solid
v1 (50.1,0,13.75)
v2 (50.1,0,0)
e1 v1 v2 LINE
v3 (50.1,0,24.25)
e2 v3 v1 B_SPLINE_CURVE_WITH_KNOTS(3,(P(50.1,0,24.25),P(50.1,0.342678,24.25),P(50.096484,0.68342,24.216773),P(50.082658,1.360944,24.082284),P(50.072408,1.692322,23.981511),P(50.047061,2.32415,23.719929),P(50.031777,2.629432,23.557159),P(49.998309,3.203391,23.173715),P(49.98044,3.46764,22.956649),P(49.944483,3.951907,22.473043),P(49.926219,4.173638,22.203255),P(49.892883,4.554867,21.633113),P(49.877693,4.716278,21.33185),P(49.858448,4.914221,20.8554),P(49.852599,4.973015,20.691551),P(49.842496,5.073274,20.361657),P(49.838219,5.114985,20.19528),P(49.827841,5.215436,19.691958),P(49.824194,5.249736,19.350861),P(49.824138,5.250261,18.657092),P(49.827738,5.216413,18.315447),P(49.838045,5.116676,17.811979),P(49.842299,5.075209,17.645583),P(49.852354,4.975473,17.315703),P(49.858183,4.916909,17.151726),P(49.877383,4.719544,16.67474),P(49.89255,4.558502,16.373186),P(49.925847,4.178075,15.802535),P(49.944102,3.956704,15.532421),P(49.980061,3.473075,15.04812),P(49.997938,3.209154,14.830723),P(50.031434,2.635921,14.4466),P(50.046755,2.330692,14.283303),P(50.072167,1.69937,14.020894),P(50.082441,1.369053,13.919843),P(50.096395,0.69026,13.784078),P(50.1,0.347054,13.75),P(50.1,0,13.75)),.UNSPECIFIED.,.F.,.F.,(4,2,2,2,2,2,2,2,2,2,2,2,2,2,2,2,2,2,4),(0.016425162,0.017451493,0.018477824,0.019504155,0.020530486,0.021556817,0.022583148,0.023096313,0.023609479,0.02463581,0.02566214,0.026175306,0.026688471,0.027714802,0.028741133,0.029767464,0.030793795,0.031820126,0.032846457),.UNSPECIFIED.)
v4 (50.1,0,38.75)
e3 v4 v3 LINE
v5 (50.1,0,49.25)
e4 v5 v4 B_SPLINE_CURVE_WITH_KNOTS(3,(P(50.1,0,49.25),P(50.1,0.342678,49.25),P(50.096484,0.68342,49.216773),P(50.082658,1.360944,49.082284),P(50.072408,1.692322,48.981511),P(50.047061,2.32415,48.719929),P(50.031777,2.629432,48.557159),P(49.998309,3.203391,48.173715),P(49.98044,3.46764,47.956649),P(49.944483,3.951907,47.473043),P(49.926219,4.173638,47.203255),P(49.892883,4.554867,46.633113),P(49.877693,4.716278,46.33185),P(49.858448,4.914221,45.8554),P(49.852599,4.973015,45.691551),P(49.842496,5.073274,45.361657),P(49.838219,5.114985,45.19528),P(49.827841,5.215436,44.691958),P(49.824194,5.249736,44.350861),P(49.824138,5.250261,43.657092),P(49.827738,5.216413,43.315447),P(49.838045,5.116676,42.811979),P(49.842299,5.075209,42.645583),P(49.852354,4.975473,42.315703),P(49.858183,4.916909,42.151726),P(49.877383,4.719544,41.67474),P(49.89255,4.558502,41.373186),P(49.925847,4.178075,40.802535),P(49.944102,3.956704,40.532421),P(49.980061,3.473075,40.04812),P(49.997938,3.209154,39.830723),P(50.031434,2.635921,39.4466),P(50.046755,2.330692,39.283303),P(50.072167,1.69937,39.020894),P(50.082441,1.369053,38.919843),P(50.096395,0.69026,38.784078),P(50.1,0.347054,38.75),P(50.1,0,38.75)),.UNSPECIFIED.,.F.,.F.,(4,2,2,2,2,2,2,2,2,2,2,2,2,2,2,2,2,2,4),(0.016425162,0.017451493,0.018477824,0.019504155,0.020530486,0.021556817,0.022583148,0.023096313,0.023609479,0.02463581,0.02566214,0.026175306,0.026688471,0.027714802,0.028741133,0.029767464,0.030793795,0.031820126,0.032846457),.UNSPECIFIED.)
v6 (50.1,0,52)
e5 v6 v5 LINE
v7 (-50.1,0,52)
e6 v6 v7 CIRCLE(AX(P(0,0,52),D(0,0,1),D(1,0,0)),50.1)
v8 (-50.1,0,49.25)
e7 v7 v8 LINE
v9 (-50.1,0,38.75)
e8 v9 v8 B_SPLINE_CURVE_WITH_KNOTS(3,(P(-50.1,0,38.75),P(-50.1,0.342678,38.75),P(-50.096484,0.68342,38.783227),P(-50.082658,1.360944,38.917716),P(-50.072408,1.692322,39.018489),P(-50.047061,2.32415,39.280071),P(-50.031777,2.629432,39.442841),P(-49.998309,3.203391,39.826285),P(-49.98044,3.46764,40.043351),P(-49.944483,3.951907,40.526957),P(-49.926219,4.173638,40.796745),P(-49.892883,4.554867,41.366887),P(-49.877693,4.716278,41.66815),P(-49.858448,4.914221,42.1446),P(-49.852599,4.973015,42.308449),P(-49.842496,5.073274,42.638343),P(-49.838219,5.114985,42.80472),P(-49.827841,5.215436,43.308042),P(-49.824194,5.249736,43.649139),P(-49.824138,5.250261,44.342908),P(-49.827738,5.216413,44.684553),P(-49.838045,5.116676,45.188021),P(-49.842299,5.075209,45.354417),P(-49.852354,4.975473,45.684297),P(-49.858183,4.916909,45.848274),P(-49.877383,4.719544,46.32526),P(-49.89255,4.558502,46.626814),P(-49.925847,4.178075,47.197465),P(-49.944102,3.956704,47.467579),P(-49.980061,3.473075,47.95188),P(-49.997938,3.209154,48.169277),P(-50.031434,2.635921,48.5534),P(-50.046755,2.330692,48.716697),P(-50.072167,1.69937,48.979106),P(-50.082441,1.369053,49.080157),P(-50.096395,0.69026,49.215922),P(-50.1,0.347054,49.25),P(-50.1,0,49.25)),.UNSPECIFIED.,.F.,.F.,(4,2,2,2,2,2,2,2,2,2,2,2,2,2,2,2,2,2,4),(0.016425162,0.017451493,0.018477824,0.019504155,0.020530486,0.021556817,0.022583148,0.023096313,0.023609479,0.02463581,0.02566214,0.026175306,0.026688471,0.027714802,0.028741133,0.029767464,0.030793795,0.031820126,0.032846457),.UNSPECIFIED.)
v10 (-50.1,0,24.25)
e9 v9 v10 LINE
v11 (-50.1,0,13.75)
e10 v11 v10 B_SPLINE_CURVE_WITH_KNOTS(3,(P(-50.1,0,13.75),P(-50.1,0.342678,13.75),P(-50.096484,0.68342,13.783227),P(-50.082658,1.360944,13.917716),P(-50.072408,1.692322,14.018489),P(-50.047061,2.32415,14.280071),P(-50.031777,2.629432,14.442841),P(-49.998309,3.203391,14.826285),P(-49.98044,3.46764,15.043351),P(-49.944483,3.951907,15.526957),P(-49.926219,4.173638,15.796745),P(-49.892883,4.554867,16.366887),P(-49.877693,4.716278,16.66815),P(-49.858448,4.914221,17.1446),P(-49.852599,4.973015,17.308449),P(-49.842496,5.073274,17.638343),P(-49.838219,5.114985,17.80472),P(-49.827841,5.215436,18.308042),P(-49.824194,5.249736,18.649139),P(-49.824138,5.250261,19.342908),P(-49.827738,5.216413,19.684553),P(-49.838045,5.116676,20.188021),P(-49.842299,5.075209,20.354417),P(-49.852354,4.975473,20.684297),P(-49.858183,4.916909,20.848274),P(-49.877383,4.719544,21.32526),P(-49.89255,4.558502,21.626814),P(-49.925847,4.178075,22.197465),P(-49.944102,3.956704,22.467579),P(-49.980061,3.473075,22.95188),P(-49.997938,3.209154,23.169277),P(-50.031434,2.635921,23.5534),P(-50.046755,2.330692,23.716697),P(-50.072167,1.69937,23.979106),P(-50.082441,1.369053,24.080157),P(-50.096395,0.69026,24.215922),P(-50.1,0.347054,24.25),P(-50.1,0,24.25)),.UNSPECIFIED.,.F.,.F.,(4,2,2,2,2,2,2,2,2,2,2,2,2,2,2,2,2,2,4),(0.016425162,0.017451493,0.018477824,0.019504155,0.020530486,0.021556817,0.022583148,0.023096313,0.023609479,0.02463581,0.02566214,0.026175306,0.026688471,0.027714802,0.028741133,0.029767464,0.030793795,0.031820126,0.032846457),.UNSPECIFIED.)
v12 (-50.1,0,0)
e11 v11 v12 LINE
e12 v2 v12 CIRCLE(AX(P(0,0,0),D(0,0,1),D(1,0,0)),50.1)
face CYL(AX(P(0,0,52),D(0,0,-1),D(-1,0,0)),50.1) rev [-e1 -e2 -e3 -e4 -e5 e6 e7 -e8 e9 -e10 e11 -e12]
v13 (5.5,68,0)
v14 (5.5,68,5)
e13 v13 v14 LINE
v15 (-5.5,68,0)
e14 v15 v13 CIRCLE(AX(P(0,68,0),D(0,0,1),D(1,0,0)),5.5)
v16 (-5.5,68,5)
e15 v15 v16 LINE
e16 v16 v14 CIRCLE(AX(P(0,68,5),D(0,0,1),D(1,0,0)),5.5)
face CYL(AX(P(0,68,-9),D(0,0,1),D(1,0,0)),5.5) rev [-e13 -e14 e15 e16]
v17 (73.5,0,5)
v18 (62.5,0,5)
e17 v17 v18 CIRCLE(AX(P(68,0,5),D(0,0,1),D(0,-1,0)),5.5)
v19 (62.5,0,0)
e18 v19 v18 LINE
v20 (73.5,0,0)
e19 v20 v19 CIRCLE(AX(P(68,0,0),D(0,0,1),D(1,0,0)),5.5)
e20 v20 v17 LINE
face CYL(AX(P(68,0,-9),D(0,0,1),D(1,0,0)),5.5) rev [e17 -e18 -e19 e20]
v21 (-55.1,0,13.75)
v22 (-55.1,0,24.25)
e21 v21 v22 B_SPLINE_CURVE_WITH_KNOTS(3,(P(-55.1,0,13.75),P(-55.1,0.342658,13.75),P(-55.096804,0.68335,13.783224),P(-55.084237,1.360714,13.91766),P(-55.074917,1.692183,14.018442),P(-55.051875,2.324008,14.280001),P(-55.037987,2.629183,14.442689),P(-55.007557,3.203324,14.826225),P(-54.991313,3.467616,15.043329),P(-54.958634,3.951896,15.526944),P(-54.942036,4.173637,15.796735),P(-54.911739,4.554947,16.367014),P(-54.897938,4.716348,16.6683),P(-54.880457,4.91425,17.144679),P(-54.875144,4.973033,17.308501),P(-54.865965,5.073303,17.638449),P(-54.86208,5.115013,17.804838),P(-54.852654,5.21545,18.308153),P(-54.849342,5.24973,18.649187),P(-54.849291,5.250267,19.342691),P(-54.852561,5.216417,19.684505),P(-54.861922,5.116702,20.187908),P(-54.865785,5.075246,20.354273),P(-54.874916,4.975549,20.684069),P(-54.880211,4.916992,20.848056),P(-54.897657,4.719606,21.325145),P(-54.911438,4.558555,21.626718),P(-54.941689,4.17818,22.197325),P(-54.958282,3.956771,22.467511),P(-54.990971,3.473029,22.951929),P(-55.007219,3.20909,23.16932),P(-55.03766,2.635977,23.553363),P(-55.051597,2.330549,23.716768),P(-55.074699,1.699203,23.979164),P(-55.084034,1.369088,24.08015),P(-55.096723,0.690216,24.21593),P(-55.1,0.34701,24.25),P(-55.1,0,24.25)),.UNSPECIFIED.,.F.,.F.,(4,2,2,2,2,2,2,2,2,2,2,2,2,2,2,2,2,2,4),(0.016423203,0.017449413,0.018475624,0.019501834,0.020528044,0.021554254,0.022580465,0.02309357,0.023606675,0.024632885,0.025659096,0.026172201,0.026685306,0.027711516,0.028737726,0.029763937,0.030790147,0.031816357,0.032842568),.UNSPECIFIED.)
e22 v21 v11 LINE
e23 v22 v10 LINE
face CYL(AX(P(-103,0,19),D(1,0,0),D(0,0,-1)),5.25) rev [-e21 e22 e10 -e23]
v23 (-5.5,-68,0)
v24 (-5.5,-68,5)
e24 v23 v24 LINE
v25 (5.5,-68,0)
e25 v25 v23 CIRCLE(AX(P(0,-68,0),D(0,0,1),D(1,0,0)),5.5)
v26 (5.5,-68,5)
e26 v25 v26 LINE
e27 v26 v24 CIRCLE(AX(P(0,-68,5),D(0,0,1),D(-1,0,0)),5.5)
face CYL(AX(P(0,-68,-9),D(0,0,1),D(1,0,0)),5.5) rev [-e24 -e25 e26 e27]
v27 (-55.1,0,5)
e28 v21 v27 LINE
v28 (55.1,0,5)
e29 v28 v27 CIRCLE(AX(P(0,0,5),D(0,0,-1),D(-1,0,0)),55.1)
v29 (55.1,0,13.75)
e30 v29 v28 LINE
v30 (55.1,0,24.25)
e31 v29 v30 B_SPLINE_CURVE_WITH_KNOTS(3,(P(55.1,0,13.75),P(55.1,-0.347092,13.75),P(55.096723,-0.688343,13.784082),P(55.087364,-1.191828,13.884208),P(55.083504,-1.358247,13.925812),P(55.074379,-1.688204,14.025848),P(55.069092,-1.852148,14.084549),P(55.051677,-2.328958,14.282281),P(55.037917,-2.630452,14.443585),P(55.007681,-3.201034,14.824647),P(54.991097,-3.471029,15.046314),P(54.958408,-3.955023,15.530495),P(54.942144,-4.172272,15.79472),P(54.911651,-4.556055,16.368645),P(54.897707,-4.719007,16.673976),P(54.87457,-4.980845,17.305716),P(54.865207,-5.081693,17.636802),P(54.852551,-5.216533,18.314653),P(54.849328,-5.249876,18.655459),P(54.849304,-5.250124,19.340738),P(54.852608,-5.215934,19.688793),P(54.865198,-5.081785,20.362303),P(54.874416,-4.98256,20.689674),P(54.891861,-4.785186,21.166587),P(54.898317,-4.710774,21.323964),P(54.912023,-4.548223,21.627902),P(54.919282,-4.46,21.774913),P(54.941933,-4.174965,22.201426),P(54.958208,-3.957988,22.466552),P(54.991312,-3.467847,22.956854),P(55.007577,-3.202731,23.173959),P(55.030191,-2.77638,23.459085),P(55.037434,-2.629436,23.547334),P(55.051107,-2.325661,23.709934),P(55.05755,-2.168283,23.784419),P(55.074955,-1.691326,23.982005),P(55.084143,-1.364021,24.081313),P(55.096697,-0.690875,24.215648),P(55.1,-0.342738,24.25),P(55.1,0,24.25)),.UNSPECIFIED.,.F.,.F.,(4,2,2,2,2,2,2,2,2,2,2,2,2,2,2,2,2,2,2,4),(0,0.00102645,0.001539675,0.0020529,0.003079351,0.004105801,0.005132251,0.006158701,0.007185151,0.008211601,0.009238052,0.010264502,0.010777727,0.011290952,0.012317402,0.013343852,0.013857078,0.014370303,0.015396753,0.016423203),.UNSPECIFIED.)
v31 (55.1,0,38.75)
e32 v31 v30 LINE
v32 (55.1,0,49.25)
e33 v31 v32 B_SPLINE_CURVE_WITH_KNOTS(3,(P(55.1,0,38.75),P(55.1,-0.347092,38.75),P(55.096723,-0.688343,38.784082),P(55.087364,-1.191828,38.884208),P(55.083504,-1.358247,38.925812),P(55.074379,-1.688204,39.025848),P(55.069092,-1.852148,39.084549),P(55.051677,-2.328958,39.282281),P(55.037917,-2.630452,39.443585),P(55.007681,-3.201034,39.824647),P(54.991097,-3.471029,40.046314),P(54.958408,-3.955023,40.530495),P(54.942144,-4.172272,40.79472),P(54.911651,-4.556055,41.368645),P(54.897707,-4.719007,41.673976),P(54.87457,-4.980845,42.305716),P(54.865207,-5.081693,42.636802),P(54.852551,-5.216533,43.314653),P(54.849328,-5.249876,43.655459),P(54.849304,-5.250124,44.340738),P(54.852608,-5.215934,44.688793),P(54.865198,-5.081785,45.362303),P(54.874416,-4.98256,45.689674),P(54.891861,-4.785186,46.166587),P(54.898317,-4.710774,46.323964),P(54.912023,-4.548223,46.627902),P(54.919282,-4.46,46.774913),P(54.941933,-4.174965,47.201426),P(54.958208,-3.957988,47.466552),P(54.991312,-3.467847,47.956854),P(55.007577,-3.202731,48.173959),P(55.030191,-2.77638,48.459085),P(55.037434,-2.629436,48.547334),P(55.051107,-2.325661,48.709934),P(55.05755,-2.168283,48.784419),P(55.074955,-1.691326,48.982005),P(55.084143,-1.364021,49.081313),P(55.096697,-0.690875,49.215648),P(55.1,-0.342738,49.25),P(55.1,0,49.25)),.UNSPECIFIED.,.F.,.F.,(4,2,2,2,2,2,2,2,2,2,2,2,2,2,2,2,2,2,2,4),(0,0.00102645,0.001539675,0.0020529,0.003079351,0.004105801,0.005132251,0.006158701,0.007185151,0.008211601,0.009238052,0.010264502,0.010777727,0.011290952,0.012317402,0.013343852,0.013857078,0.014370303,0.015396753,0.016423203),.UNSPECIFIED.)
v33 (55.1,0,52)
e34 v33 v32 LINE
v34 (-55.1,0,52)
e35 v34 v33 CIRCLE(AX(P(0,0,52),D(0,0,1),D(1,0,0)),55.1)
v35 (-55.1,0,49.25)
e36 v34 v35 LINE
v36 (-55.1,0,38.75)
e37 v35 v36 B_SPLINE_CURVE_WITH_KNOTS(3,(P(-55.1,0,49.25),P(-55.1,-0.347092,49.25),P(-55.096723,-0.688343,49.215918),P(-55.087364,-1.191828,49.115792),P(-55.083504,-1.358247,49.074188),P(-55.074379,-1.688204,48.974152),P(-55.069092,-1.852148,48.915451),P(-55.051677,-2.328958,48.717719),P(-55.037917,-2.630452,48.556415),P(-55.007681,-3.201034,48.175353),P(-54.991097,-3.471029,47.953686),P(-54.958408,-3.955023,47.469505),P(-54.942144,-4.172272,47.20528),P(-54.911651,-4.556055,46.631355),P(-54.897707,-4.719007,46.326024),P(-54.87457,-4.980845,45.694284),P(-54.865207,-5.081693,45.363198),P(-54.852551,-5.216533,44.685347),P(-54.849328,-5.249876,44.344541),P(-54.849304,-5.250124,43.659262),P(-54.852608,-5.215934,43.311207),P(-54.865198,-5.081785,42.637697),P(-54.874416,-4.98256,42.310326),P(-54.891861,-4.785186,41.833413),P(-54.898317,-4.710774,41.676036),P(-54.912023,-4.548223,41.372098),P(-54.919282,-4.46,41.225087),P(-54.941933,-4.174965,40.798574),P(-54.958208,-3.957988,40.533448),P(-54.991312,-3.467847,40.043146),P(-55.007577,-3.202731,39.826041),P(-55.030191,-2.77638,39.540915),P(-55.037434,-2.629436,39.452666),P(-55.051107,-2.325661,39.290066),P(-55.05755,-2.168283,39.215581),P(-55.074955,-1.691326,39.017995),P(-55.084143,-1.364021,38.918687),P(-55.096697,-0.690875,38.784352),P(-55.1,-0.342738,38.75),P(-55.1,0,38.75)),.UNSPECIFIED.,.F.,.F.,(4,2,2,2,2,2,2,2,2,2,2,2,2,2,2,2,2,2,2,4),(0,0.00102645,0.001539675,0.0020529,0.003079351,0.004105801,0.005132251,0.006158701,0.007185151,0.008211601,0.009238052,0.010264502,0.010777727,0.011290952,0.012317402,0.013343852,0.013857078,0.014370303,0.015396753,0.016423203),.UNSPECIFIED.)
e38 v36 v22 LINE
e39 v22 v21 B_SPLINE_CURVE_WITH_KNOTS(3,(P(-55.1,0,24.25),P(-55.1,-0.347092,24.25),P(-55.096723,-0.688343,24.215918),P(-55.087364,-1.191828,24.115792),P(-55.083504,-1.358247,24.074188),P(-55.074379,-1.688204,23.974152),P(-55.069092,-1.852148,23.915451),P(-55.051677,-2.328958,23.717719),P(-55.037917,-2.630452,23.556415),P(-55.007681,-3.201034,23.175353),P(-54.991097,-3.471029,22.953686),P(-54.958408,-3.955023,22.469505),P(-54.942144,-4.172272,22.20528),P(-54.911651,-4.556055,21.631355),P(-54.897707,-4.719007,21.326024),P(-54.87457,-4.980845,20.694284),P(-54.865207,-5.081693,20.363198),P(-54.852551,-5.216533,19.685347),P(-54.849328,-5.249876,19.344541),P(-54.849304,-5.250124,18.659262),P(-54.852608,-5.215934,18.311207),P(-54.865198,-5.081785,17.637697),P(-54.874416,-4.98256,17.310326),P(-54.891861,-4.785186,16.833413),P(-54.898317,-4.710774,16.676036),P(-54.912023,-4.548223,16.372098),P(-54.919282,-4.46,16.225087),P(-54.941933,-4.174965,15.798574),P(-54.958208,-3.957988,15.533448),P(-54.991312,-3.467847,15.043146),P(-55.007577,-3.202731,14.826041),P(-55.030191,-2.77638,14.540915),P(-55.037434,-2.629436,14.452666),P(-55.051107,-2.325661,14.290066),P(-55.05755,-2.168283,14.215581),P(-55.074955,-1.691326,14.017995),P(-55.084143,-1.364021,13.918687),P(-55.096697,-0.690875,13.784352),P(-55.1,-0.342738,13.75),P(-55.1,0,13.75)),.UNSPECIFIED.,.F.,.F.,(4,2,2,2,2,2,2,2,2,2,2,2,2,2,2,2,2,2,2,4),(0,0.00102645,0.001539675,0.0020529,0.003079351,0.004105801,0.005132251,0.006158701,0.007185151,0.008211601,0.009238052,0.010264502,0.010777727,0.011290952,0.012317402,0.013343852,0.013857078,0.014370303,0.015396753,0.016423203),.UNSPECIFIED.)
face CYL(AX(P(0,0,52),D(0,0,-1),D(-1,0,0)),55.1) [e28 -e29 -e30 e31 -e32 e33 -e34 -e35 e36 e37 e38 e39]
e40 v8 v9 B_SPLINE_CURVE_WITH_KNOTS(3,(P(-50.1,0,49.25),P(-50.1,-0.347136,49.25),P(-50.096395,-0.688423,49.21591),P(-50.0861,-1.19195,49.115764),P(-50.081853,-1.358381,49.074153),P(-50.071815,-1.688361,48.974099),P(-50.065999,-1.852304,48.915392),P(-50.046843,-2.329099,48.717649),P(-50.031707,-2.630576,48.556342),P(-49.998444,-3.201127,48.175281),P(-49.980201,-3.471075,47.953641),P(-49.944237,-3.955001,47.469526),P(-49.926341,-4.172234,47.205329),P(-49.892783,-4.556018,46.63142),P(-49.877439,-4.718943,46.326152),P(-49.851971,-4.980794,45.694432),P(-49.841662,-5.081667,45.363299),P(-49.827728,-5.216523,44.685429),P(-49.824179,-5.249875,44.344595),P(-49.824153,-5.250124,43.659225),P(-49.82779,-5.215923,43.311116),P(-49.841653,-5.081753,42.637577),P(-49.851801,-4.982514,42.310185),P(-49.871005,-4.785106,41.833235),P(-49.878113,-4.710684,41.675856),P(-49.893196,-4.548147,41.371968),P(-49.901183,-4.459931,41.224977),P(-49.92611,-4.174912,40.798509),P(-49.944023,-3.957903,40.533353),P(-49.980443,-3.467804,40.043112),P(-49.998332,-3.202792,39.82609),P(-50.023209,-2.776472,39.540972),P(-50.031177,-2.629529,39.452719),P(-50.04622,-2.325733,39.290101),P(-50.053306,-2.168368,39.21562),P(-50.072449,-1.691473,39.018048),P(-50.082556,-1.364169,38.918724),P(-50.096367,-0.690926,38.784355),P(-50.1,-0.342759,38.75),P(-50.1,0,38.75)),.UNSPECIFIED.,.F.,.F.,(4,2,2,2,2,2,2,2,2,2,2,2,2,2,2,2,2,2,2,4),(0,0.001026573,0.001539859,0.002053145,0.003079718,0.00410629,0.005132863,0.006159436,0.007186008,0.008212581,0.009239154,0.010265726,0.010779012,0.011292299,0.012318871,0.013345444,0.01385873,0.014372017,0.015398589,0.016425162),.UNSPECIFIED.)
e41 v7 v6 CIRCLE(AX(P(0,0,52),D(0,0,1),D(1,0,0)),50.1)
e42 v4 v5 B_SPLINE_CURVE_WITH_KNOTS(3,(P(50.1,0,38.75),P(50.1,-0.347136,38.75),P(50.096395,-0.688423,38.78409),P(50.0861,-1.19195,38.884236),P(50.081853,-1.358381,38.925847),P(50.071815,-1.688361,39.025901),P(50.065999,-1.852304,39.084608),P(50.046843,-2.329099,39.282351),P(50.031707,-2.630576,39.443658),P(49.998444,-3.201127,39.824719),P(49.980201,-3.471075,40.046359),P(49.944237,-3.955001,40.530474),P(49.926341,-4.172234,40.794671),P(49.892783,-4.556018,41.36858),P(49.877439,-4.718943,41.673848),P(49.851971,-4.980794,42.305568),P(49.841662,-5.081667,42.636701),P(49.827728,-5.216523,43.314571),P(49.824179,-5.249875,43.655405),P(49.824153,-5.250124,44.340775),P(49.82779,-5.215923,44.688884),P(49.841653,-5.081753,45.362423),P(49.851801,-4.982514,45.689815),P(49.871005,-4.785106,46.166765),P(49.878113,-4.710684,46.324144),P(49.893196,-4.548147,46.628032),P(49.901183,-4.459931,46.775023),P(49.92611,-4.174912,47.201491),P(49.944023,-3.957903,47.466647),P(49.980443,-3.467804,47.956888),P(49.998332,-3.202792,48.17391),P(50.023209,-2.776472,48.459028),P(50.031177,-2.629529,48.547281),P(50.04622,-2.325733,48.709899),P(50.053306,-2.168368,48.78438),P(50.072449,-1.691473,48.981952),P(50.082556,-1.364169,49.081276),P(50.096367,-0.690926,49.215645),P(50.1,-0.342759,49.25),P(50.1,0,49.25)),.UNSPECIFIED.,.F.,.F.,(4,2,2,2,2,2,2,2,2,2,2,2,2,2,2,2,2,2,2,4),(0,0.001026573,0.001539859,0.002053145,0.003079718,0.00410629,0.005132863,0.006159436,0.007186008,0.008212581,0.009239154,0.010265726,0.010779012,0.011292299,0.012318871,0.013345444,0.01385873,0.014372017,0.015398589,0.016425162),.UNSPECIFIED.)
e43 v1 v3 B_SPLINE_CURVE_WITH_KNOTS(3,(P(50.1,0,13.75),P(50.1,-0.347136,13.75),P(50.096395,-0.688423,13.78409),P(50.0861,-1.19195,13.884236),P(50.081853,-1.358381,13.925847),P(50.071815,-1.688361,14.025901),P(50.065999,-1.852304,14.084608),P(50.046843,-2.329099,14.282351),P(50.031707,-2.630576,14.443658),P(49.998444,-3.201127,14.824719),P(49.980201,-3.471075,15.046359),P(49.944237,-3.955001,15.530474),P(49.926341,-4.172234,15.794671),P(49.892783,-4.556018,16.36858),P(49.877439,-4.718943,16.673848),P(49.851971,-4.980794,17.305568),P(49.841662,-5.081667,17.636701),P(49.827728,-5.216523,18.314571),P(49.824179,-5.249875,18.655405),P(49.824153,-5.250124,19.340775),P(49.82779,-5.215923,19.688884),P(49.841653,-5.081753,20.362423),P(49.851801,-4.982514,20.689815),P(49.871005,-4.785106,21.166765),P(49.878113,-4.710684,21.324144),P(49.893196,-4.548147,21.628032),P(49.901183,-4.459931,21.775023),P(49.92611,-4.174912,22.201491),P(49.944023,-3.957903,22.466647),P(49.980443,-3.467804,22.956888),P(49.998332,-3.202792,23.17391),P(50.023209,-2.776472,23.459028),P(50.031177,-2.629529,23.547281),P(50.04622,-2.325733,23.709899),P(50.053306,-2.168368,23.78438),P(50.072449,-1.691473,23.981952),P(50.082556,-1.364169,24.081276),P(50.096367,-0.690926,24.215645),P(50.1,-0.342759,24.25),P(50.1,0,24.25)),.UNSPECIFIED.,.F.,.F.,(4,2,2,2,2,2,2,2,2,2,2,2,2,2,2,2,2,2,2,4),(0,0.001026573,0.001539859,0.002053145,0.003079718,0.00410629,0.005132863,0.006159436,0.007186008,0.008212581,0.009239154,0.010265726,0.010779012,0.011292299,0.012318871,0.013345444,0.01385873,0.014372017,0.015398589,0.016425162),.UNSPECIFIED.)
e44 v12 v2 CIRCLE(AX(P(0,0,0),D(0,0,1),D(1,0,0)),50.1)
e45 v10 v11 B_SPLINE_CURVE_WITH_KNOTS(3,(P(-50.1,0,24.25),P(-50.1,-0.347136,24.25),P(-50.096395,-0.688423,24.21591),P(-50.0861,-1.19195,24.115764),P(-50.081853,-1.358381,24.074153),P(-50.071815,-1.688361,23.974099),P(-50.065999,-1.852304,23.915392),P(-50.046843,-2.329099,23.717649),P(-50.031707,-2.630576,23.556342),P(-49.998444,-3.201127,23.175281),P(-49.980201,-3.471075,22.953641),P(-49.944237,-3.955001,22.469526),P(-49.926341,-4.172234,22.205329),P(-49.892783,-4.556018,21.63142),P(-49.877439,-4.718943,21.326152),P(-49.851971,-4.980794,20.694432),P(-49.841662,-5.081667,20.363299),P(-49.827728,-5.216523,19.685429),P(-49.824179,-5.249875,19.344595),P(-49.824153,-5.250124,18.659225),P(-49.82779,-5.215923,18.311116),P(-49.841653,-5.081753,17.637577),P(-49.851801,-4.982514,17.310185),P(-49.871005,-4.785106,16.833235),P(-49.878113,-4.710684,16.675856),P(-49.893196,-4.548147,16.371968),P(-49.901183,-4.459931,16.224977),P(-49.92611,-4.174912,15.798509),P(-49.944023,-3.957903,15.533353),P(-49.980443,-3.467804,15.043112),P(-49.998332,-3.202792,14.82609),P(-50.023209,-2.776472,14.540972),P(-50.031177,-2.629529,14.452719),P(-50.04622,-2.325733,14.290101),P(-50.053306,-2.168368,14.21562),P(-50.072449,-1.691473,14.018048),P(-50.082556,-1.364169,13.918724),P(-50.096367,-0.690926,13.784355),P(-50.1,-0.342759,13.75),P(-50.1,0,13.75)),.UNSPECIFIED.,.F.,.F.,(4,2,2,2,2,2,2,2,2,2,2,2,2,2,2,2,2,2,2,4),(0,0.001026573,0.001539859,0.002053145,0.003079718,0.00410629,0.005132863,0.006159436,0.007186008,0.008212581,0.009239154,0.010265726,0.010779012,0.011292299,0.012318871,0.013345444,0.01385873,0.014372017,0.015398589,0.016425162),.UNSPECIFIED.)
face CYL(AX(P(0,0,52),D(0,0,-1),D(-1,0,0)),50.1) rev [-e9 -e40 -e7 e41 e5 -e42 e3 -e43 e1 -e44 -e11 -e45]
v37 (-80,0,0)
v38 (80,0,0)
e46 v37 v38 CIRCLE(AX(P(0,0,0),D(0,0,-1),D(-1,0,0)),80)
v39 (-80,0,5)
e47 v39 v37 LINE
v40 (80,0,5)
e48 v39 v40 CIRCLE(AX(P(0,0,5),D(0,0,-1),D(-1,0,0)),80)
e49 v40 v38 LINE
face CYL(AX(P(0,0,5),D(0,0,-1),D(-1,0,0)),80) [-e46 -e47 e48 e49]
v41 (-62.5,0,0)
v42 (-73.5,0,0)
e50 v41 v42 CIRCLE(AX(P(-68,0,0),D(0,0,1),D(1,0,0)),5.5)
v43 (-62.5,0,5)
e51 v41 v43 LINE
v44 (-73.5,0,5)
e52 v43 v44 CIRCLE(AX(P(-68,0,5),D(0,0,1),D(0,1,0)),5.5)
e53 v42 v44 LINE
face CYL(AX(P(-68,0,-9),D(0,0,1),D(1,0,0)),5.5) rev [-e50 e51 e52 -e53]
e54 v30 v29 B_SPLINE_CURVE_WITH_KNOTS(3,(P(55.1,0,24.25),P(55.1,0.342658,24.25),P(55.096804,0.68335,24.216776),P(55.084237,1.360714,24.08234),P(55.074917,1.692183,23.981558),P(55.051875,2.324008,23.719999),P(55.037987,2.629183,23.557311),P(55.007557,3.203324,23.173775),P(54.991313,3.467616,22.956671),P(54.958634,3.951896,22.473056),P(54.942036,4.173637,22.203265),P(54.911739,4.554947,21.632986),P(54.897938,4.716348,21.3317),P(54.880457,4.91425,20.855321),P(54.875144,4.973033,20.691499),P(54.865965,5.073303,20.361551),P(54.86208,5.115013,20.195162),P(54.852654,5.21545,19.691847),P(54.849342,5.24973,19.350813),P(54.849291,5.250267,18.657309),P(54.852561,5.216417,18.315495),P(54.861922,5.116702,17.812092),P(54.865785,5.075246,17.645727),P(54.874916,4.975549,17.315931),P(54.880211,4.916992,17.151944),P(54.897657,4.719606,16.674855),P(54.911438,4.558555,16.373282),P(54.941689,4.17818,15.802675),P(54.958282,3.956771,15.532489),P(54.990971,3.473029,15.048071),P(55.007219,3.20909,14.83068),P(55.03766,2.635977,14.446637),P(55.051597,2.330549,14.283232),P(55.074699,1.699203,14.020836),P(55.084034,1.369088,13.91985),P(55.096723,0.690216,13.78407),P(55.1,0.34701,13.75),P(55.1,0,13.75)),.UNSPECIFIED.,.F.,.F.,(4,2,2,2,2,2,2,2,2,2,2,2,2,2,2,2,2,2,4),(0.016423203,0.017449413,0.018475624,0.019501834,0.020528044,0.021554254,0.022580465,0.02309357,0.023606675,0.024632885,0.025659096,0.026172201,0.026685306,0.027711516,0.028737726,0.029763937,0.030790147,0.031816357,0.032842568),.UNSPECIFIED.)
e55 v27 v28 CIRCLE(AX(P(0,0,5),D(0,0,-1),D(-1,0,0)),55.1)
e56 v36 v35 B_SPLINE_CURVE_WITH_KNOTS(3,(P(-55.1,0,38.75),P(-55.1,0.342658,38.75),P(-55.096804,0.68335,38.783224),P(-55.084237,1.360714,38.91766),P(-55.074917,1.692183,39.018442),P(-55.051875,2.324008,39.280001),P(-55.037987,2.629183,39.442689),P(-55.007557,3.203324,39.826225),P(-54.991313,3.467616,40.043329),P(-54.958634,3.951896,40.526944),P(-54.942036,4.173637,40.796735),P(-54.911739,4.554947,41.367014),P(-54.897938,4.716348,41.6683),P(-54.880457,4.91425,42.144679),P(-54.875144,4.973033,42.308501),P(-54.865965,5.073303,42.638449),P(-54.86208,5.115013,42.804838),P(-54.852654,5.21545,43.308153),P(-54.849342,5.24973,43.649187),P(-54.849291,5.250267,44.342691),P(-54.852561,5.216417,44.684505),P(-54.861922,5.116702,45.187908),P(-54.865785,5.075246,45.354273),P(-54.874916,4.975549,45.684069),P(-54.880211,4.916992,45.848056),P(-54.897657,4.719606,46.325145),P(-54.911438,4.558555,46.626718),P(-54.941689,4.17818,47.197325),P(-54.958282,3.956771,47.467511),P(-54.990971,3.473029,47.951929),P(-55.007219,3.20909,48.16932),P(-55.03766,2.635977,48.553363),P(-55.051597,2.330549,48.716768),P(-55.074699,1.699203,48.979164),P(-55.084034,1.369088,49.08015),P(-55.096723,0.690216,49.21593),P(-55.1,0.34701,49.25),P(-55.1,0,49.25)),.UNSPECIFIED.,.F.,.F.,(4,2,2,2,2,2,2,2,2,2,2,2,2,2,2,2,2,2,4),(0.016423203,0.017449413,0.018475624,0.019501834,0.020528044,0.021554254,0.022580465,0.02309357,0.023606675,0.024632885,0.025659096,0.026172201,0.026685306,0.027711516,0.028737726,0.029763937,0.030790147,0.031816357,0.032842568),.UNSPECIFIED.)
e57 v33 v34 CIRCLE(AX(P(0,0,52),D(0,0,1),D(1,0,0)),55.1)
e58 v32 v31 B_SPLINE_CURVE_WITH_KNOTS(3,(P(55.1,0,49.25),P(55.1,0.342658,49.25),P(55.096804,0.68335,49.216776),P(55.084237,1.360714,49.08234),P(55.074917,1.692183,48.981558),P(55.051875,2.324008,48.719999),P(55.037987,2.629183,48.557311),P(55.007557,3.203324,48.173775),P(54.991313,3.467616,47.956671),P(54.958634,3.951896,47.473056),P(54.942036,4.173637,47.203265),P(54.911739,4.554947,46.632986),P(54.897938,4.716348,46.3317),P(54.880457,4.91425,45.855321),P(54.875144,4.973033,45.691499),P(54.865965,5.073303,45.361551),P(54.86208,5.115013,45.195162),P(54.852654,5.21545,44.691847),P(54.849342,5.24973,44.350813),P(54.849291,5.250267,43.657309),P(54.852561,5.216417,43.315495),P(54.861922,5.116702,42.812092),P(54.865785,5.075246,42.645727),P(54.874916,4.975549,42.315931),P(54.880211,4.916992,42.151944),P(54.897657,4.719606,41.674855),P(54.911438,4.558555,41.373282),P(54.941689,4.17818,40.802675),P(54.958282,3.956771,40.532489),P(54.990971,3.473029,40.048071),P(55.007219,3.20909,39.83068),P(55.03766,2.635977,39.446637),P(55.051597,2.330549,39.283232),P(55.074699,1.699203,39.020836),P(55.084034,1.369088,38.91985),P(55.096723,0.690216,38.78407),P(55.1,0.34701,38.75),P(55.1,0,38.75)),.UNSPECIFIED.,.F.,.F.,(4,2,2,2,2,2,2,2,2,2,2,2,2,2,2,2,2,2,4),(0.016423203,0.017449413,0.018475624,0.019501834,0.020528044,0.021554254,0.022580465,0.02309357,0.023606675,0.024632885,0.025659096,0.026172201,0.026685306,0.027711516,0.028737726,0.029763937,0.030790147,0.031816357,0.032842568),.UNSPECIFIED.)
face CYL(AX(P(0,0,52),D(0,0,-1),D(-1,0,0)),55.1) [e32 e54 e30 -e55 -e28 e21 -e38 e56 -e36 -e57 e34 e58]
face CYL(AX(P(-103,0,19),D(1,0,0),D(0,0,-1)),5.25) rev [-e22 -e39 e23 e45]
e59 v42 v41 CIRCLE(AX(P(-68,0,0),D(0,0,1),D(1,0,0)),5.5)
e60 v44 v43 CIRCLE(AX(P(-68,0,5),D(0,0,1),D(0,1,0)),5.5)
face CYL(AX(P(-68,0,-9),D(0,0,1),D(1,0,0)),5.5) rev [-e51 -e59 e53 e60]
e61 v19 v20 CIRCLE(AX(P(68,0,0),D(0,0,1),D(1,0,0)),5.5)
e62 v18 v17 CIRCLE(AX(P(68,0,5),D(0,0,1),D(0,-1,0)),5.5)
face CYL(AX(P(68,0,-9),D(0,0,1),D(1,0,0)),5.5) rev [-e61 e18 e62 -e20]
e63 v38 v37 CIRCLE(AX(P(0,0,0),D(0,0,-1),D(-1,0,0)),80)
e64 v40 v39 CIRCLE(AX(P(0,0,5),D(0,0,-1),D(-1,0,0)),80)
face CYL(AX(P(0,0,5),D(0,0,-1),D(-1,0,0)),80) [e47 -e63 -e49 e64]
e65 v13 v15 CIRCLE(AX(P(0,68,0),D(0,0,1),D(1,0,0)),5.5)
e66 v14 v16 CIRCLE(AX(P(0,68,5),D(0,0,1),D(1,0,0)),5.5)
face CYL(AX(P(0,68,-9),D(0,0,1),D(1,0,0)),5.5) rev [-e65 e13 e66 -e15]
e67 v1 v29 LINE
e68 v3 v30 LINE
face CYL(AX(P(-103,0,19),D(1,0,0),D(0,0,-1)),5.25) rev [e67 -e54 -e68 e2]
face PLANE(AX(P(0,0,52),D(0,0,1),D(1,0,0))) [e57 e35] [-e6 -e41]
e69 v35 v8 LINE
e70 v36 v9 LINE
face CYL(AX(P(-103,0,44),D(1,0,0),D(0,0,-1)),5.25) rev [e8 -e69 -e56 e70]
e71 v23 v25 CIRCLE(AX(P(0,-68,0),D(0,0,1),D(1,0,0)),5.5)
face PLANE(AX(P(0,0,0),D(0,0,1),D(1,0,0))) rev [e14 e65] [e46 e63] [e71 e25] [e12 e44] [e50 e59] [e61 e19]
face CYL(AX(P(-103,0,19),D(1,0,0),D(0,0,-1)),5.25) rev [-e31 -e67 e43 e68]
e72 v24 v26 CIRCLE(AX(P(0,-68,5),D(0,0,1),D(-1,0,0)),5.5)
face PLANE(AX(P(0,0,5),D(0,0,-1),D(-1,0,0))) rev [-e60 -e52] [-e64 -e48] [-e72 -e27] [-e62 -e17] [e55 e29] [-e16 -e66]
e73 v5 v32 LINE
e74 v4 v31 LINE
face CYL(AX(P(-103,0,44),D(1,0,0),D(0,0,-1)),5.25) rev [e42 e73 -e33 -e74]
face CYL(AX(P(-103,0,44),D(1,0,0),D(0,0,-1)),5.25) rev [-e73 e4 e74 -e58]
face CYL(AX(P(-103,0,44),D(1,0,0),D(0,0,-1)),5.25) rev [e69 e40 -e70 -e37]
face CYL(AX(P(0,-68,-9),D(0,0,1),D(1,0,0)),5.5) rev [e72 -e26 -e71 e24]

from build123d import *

# Parameters (mm, degrees)
SKETCH_1_R               = 55.1
SKETCH_1_R_2             = 50.1
EXTRUDE_1_DEPTH          = 52
SKETCH_2_R               = 80
EXTRUDE_2_DEPTH          = 5
SKETCH_3_R               = 5.5
CUT_EXTRUDE_1_DEPTH      = 14
PATTERN_CIRCULAR_1_COUNT = 4
CUT_EXTRUDE_START        = -66
SKETCH_4_R               = 50.1
CUT_EXTRUDE_2_DEPTH      = 66
SKETCH_6_R               = 5.25
CUT_EXTRUDE_3_DEPTH      = 103


with BuildPart() as part:
    # 草图1 → 凸台-拉伸1 (new body)
    with BuildSketch(Plane.XY):
        with Locations(Location((0, 0, 0), (0, 0, 180))):
            Circle(SKETCH_1_R)
        with Locations(Location((0, 0, 0), (0, 0, 180))):
            Circle(SKETCH_1_R_2, mode=Mode.SUBTRACT)
    extrude(amount=EXTRUDE_1_DEPTH)

    # 草图2 → 凸台-拉伸2 (add)
    with BuildSketch(Plane(origin=(0, 0, 0), x_dir=(-1, 0, 0), z_dir=(0, 0, -1))):
        Circle(SKETCH_2_R)
    extrude(amount=-EXTRUDE_2_DEPTH)

    # 草图3 → 切除-拉伸1 (cut)
    with BuildSketch(Plane.XY.offset(5)):
        with Locations((0, 68)):
            Circle(SKETCH_3_R)
    cut_extrude_1 = extrude(amount=-CUT_EXTRUDE_1_DEPTH, mode=Mode.SUBTRACT)

    # 阵列(圆周)1: 切除-拉伸1 ×4 about axis
    pattern_circular_1_axis = Axis((0, 0, 0), (0, 0, 1))
    for i in range(1, PATTERN_CIRCULAR_1_COUNT):
        add(cut_extrude_1.rotate(pattern_circular_1_axis, i * 360 / PATTERN_CIRCULAR_1_COUNT), mode=Mode.SUBTRACT)

    # 草图4 → 切除-拉伸2 (cut)
    with BuildSketch(Plane.XY.offset(5).offset(CUT_EXTRUDE_START)):
        with Locations(Location((0, 0, 0), (0, 0, 180))):
            Circle(SKETCH_4_R)
    extrude(amount=CUT_EXTRUDE_2_DEPTH, mode=Mode.SUBTRACT)

    # 草图6 → 切除-拉伸3 (cut, symmetric)
    with BuildSketch(Plane(origin=(0, 0, 0), x_dir=(0, -1, 0), z_dir=(1, 0, 0))):
        with Locations(Location((0, -19, 0), (0, 0, 90))):
            Circle(SKETCH_6_R)
        with Locations(Location((0, -44, 0), (0, 0, 90))):
            Circle(SKETCH_6_R)
    extrude(amount=CUT_EXTRUDE_3_DEPTH, both=True, mode=Mode.SUBTRACT)


solid = part.part
